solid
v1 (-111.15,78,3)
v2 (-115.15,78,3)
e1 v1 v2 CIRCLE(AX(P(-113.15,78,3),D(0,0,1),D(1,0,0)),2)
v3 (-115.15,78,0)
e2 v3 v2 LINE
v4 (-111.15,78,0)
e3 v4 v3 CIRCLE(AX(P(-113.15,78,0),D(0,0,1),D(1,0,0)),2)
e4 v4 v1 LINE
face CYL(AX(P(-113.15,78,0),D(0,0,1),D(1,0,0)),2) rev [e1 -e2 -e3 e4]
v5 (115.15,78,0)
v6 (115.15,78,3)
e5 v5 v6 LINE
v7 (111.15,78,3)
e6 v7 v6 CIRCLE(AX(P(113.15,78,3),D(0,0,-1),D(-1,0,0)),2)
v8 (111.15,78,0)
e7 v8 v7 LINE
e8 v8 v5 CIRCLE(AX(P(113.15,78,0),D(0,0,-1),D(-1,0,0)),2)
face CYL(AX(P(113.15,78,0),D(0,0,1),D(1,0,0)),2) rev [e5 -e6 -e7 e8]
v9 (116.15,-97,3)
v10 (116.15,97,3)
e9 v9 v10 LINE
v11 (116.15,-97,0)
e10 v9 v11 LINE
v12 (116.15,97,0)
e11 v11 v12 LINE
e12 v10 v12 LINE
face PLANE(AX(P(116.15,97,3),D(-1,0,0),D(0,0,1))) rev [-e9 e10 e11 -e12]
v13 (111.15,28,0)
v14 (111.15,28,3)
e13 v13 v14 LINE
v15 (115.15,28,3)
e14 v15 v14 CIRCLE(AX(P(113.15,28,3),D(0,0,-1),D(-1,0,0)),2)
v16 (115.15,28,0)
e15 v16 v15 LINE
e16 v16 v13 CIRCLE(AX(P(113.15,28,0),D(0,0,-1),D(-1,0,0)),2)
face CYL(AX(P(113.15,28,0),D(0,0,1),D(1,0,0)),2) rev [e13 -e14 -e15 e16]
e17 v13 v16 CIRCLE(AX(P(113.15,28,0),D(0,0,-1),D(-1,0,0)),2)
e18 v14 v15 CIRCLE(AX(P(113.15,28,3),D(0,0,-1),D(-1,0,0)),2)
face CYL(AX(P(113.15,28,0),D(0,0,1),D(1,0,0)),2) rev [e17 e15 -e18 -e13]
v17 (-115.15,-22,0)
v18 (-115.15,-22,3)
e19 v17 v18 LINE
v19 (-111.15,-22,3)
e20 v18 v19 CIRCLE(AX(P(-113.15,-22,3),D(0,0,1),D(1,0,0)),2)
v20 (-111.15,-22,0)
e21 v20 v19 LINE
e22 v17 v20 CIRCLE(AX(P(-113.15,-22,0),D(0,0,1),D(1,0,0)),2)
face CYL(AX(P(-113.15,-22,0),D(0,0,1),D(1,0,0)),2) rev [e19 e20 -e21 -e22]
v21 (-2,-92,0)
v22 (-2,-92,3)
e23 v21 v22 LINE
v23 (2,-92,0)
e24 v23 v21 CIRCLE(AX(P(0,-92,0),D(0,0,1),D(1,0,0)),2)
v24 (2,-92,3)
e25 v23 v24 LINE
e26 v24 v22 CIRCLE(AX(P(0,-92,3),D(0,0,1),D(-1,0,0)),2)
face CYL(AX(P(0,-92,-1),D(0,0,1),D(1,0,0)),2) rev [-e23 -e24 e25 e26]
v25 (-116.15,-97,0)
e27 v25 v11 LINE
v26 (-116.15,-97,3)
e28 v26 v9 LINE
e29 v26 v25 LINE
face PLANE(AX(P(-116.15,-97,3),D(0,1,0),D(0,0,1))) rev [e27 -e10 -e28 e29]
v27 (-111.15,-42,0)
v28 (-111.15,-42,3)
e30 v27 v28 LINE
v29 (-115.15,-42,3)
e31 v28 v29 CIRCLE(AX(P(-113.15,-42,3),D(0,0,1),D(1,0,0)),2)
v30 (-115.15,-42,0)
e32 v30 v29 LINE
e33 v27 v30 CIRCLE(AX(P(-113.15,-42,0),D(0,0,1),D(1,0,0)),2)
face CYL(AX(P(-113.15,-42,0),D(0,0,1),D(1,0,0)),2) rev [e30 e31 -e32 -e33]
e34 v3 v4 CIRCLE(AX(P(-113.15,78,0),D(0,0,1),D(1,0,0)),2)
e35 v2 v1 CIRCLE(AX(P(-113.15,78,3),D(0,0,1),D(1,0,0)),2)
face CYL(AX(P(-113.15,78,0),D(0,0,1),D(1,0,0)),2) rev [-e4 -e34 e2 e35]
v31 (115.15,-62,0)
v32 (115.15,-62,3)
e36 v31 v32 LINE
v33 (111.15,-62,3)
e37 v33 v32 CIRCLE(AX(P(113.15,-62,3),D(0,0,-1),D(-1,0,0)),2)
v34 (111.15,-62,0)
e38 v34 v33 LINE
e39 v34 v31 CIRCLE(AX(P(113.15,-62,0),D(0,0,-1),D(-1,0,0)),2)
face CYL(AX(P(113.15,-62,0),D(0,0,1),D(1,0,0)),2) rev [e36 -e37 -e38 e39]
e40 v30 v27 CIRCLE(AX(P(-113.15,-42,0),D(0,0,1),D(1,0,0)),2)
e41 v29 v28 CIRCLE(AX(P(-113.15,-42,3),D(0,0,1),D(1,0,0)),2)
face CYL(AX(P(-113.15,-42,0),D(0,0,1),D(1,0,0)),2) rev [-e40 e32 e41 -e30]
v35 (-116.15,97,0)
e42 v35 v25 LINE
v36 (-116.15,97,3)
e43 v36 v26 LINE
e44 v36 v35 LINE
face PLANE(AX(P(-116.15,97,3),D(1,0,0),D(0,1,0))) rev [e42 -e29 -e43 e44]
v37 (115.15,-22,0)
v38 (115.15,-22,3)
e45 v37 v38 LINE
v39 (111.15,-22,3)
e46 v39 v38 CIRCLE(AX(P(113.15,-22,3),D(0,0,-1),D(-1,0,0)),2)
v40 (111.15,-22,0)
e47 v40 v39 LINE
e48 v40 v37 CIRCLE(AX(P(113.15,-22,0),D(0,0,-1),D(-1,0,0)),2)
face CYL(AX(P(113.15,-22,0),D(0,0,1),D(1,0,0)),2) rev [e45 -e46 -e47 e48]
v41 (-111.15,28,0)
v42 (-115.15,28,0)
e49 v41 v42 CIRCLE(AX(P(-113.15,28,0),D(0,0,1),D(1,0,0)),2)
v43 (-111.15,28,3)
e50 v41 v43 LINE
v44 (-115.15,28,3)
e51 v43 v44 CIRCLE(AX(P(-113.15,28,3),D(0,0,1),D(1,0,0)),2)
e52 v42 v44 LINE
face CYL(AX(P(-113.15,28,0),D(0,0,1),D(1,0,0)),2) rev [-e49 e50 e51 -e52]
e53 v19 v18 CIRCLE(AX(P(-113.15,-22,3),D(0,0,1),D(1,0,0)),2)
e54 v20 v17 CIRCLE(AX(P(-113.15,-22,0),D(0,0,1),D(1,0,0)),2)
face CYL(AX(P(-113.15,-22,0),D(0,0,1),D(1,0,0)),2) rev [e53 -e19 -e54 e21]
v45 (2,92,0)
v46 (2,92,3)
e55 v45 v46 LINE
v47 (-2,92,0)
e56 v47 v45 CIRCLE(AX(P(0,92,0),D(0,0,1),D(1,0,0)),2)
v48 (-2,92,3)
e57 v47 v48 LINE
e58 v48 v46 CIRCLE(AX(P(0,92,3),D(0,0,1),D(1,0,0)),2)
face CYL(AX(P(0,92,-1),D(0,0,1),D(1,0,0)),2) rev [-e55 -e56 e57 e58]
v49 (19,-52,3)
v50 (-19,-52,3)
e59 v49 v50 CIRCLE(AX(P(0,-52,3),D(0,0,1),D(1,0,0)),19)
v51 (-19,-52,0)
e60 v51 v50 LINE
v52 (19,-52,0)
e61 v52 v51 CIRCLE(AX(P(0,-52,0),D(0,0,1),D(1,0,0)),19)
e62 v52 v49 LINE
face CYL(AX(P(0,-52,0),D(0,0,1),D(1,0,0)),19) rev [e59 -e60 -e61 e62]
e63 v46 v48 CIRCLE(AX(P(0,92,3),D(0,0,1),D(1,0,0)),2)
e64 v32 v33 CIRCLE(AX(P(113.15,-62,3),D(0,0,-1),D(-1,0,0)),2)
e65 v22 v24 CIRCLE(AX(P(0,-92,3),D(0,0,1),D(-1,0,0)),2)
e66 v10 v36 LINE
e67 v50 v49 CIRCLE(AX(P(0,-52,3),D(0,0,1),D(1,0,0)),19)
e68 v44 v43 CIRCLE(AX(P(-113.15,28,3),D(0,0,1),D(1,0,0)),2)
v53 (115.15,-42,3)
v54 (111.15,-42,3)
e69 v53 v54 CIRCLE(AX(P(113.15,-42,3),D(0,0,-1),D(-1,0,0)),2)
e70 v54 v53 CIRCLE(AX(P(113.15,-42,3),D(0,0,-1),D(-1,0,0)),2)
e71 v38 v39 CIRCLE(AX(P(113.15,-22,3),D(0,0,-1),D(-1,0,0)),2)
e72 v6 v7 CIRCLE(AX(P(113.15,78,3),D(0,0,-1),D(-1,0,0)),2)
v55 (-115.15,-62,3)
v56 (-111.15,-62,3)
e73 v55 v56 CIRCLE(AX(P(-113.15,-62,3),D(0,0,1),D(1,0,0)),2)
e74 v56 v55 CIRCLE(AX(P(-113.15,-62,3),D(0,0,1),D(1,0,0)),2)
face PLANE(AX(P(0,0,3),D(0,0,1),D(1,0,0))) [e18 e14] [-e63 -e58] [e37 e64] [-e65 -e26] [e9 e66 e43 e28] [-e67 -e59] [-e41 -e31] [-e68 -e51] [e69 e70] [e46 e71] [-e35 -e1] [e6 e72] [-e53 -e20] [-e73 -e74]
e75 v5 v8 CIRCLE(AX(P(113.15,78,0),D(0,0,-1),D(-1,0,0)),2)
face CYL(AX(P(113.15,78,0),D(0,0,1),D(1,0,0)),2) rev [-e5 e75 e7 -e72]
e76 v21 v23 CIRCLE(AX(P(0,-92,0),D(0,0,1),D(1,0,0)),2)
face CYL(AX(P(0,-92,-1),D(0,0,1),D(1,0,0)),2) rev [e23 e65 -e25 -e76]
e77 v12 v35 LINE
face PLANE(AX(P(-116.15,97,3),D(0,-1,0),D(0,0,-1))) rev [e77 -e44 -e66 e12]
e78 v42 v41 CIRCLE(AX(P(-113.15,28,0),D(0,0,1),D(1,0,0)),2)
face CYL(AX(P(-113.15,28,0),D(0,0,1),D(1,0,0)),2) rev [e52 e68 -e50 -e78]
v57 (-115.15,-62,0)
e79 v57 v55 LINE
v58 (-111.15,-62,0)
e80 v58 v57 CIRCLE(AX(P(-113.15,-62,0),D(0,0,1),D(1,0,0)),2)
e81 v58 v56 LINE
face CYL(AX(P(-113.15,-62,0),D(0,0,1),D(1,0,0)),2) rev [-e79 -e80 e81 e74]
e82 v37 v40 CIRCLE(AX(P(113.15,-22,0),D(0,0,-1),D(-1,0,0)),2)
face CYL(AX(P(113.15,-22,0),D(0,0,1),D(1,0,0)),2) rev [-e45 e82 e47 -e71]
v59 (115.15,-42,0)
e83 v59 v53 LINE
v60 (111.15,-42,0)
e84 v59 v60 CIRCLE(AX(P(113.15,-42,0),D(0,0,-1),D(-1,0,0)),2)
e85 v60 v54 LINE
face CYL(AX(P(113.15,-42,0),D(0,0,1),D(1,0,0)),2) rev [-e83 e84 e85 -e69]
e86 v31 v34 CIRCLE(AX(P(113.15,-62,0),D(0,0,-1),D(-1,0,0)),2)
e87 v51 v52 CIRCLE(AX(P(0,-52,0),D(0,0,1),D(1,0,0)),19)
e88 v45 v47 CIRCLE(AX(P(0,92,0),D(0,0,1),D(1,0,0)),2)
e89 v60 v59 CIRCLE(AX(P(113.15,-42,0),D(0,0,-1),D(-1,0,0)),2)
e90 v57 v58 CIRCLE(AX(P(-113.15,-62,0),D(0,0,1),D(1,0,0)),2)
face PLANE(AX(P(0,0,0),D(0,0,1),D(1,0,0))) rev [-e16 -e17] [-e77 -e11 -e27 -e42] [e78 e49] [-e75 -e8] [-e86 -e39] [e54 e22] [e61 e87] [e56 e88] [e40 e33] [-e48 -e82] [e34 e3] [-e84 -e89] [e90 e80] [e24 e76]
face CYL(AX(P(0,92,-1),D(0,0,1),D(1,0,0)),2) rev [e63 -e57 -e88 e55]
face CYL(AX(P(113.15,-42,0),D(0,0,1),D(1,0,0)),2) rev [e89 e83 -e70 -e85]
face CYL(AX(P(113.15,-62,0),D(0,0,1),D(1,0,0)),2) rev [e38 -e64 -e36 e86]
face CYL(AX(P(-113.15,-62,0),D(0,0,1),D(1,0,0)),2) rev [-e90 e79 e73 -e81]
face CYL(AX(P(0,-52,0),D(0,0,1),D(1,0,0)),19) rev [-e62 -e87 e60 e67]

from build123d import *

# Parameters (mm, degrees)
SKETCH1_W           = 232.3
SKETCH1_H           = 194
BOSS_EXTRUDE1_DEPTH = 3
SKETCH2_R           = 19
CUT_EXTRUDE1_DEPTH  = 3
SKETCH3_R           = 2
CUT_EXTRUDE2_DEPTH  = 4
SKETCH4_R           = 2
CUT_EXTRUDE3_DEPTH  = 152.356607058


with BuildPart() as part:
    # Sketch1 → Boss-Extrude1 (new body)
    with BuildSketch(Plane.XY):
        Rectangle(SKETCH1_W, SKETCH1_H)
    extrude(amount=BOSS_EXTRUDE1_DEPTH)

    # Sketch2 → Cut-Extrude1 (cut)
    with BuildSketch(Plane.XY.offset(3)):
        with Locations((0, -52)):
            Circle(SKETCH2_R)
    extrude(amount=-CUT_EXTRUDE1_DEPTH, mode=Mode.SUBTRACT)

    # Sketch3 → Cut-Extrude2 (cut)
    with BuildSketch(Plane.XY.offset(3)):
        with Locations((0, 92)):
            Circle(SKETCH3_R)
        with Locations((0, -92)):
            Circle(SKETCH3_R)
    extrude(amount=-CUT_EXTRUDE2_DEPTH, mode=Mode.SUBTRACT)

    # Sketch4 → Cut-Extrude3 (cut, through all)
    with BuildSketch(Plane.XY.offset(3)):
        with Locations((-113.15, 78)):
            Circle(SKETCH4_R)
        with Locations((-113.15, 28)):
            Circle(SKETCH4_R)
        with Locations((-113.15, -22)):
            Circle(SKETCH4_R)
        with Locations((-113.15, -42)):
            Circle(SKETCH4_R)
        with Locations((-113.15, -62)):
            Circle(SKETCH4_R)
    cut_extrude3 = extrude(amount=-CUT_EXTRUDE3_DEPTH, mode=Mode.SUBTRACT)

    # Mirror1: Cut-Extrude3 across plane
    add(cut_extrude3.mirror(Plane(origin=(0, 0, 0), x_dir=(0, 0, 1), z_dir=(1, 0, 0))), mode=Mode.SUBTRACT)


solid = part.part
